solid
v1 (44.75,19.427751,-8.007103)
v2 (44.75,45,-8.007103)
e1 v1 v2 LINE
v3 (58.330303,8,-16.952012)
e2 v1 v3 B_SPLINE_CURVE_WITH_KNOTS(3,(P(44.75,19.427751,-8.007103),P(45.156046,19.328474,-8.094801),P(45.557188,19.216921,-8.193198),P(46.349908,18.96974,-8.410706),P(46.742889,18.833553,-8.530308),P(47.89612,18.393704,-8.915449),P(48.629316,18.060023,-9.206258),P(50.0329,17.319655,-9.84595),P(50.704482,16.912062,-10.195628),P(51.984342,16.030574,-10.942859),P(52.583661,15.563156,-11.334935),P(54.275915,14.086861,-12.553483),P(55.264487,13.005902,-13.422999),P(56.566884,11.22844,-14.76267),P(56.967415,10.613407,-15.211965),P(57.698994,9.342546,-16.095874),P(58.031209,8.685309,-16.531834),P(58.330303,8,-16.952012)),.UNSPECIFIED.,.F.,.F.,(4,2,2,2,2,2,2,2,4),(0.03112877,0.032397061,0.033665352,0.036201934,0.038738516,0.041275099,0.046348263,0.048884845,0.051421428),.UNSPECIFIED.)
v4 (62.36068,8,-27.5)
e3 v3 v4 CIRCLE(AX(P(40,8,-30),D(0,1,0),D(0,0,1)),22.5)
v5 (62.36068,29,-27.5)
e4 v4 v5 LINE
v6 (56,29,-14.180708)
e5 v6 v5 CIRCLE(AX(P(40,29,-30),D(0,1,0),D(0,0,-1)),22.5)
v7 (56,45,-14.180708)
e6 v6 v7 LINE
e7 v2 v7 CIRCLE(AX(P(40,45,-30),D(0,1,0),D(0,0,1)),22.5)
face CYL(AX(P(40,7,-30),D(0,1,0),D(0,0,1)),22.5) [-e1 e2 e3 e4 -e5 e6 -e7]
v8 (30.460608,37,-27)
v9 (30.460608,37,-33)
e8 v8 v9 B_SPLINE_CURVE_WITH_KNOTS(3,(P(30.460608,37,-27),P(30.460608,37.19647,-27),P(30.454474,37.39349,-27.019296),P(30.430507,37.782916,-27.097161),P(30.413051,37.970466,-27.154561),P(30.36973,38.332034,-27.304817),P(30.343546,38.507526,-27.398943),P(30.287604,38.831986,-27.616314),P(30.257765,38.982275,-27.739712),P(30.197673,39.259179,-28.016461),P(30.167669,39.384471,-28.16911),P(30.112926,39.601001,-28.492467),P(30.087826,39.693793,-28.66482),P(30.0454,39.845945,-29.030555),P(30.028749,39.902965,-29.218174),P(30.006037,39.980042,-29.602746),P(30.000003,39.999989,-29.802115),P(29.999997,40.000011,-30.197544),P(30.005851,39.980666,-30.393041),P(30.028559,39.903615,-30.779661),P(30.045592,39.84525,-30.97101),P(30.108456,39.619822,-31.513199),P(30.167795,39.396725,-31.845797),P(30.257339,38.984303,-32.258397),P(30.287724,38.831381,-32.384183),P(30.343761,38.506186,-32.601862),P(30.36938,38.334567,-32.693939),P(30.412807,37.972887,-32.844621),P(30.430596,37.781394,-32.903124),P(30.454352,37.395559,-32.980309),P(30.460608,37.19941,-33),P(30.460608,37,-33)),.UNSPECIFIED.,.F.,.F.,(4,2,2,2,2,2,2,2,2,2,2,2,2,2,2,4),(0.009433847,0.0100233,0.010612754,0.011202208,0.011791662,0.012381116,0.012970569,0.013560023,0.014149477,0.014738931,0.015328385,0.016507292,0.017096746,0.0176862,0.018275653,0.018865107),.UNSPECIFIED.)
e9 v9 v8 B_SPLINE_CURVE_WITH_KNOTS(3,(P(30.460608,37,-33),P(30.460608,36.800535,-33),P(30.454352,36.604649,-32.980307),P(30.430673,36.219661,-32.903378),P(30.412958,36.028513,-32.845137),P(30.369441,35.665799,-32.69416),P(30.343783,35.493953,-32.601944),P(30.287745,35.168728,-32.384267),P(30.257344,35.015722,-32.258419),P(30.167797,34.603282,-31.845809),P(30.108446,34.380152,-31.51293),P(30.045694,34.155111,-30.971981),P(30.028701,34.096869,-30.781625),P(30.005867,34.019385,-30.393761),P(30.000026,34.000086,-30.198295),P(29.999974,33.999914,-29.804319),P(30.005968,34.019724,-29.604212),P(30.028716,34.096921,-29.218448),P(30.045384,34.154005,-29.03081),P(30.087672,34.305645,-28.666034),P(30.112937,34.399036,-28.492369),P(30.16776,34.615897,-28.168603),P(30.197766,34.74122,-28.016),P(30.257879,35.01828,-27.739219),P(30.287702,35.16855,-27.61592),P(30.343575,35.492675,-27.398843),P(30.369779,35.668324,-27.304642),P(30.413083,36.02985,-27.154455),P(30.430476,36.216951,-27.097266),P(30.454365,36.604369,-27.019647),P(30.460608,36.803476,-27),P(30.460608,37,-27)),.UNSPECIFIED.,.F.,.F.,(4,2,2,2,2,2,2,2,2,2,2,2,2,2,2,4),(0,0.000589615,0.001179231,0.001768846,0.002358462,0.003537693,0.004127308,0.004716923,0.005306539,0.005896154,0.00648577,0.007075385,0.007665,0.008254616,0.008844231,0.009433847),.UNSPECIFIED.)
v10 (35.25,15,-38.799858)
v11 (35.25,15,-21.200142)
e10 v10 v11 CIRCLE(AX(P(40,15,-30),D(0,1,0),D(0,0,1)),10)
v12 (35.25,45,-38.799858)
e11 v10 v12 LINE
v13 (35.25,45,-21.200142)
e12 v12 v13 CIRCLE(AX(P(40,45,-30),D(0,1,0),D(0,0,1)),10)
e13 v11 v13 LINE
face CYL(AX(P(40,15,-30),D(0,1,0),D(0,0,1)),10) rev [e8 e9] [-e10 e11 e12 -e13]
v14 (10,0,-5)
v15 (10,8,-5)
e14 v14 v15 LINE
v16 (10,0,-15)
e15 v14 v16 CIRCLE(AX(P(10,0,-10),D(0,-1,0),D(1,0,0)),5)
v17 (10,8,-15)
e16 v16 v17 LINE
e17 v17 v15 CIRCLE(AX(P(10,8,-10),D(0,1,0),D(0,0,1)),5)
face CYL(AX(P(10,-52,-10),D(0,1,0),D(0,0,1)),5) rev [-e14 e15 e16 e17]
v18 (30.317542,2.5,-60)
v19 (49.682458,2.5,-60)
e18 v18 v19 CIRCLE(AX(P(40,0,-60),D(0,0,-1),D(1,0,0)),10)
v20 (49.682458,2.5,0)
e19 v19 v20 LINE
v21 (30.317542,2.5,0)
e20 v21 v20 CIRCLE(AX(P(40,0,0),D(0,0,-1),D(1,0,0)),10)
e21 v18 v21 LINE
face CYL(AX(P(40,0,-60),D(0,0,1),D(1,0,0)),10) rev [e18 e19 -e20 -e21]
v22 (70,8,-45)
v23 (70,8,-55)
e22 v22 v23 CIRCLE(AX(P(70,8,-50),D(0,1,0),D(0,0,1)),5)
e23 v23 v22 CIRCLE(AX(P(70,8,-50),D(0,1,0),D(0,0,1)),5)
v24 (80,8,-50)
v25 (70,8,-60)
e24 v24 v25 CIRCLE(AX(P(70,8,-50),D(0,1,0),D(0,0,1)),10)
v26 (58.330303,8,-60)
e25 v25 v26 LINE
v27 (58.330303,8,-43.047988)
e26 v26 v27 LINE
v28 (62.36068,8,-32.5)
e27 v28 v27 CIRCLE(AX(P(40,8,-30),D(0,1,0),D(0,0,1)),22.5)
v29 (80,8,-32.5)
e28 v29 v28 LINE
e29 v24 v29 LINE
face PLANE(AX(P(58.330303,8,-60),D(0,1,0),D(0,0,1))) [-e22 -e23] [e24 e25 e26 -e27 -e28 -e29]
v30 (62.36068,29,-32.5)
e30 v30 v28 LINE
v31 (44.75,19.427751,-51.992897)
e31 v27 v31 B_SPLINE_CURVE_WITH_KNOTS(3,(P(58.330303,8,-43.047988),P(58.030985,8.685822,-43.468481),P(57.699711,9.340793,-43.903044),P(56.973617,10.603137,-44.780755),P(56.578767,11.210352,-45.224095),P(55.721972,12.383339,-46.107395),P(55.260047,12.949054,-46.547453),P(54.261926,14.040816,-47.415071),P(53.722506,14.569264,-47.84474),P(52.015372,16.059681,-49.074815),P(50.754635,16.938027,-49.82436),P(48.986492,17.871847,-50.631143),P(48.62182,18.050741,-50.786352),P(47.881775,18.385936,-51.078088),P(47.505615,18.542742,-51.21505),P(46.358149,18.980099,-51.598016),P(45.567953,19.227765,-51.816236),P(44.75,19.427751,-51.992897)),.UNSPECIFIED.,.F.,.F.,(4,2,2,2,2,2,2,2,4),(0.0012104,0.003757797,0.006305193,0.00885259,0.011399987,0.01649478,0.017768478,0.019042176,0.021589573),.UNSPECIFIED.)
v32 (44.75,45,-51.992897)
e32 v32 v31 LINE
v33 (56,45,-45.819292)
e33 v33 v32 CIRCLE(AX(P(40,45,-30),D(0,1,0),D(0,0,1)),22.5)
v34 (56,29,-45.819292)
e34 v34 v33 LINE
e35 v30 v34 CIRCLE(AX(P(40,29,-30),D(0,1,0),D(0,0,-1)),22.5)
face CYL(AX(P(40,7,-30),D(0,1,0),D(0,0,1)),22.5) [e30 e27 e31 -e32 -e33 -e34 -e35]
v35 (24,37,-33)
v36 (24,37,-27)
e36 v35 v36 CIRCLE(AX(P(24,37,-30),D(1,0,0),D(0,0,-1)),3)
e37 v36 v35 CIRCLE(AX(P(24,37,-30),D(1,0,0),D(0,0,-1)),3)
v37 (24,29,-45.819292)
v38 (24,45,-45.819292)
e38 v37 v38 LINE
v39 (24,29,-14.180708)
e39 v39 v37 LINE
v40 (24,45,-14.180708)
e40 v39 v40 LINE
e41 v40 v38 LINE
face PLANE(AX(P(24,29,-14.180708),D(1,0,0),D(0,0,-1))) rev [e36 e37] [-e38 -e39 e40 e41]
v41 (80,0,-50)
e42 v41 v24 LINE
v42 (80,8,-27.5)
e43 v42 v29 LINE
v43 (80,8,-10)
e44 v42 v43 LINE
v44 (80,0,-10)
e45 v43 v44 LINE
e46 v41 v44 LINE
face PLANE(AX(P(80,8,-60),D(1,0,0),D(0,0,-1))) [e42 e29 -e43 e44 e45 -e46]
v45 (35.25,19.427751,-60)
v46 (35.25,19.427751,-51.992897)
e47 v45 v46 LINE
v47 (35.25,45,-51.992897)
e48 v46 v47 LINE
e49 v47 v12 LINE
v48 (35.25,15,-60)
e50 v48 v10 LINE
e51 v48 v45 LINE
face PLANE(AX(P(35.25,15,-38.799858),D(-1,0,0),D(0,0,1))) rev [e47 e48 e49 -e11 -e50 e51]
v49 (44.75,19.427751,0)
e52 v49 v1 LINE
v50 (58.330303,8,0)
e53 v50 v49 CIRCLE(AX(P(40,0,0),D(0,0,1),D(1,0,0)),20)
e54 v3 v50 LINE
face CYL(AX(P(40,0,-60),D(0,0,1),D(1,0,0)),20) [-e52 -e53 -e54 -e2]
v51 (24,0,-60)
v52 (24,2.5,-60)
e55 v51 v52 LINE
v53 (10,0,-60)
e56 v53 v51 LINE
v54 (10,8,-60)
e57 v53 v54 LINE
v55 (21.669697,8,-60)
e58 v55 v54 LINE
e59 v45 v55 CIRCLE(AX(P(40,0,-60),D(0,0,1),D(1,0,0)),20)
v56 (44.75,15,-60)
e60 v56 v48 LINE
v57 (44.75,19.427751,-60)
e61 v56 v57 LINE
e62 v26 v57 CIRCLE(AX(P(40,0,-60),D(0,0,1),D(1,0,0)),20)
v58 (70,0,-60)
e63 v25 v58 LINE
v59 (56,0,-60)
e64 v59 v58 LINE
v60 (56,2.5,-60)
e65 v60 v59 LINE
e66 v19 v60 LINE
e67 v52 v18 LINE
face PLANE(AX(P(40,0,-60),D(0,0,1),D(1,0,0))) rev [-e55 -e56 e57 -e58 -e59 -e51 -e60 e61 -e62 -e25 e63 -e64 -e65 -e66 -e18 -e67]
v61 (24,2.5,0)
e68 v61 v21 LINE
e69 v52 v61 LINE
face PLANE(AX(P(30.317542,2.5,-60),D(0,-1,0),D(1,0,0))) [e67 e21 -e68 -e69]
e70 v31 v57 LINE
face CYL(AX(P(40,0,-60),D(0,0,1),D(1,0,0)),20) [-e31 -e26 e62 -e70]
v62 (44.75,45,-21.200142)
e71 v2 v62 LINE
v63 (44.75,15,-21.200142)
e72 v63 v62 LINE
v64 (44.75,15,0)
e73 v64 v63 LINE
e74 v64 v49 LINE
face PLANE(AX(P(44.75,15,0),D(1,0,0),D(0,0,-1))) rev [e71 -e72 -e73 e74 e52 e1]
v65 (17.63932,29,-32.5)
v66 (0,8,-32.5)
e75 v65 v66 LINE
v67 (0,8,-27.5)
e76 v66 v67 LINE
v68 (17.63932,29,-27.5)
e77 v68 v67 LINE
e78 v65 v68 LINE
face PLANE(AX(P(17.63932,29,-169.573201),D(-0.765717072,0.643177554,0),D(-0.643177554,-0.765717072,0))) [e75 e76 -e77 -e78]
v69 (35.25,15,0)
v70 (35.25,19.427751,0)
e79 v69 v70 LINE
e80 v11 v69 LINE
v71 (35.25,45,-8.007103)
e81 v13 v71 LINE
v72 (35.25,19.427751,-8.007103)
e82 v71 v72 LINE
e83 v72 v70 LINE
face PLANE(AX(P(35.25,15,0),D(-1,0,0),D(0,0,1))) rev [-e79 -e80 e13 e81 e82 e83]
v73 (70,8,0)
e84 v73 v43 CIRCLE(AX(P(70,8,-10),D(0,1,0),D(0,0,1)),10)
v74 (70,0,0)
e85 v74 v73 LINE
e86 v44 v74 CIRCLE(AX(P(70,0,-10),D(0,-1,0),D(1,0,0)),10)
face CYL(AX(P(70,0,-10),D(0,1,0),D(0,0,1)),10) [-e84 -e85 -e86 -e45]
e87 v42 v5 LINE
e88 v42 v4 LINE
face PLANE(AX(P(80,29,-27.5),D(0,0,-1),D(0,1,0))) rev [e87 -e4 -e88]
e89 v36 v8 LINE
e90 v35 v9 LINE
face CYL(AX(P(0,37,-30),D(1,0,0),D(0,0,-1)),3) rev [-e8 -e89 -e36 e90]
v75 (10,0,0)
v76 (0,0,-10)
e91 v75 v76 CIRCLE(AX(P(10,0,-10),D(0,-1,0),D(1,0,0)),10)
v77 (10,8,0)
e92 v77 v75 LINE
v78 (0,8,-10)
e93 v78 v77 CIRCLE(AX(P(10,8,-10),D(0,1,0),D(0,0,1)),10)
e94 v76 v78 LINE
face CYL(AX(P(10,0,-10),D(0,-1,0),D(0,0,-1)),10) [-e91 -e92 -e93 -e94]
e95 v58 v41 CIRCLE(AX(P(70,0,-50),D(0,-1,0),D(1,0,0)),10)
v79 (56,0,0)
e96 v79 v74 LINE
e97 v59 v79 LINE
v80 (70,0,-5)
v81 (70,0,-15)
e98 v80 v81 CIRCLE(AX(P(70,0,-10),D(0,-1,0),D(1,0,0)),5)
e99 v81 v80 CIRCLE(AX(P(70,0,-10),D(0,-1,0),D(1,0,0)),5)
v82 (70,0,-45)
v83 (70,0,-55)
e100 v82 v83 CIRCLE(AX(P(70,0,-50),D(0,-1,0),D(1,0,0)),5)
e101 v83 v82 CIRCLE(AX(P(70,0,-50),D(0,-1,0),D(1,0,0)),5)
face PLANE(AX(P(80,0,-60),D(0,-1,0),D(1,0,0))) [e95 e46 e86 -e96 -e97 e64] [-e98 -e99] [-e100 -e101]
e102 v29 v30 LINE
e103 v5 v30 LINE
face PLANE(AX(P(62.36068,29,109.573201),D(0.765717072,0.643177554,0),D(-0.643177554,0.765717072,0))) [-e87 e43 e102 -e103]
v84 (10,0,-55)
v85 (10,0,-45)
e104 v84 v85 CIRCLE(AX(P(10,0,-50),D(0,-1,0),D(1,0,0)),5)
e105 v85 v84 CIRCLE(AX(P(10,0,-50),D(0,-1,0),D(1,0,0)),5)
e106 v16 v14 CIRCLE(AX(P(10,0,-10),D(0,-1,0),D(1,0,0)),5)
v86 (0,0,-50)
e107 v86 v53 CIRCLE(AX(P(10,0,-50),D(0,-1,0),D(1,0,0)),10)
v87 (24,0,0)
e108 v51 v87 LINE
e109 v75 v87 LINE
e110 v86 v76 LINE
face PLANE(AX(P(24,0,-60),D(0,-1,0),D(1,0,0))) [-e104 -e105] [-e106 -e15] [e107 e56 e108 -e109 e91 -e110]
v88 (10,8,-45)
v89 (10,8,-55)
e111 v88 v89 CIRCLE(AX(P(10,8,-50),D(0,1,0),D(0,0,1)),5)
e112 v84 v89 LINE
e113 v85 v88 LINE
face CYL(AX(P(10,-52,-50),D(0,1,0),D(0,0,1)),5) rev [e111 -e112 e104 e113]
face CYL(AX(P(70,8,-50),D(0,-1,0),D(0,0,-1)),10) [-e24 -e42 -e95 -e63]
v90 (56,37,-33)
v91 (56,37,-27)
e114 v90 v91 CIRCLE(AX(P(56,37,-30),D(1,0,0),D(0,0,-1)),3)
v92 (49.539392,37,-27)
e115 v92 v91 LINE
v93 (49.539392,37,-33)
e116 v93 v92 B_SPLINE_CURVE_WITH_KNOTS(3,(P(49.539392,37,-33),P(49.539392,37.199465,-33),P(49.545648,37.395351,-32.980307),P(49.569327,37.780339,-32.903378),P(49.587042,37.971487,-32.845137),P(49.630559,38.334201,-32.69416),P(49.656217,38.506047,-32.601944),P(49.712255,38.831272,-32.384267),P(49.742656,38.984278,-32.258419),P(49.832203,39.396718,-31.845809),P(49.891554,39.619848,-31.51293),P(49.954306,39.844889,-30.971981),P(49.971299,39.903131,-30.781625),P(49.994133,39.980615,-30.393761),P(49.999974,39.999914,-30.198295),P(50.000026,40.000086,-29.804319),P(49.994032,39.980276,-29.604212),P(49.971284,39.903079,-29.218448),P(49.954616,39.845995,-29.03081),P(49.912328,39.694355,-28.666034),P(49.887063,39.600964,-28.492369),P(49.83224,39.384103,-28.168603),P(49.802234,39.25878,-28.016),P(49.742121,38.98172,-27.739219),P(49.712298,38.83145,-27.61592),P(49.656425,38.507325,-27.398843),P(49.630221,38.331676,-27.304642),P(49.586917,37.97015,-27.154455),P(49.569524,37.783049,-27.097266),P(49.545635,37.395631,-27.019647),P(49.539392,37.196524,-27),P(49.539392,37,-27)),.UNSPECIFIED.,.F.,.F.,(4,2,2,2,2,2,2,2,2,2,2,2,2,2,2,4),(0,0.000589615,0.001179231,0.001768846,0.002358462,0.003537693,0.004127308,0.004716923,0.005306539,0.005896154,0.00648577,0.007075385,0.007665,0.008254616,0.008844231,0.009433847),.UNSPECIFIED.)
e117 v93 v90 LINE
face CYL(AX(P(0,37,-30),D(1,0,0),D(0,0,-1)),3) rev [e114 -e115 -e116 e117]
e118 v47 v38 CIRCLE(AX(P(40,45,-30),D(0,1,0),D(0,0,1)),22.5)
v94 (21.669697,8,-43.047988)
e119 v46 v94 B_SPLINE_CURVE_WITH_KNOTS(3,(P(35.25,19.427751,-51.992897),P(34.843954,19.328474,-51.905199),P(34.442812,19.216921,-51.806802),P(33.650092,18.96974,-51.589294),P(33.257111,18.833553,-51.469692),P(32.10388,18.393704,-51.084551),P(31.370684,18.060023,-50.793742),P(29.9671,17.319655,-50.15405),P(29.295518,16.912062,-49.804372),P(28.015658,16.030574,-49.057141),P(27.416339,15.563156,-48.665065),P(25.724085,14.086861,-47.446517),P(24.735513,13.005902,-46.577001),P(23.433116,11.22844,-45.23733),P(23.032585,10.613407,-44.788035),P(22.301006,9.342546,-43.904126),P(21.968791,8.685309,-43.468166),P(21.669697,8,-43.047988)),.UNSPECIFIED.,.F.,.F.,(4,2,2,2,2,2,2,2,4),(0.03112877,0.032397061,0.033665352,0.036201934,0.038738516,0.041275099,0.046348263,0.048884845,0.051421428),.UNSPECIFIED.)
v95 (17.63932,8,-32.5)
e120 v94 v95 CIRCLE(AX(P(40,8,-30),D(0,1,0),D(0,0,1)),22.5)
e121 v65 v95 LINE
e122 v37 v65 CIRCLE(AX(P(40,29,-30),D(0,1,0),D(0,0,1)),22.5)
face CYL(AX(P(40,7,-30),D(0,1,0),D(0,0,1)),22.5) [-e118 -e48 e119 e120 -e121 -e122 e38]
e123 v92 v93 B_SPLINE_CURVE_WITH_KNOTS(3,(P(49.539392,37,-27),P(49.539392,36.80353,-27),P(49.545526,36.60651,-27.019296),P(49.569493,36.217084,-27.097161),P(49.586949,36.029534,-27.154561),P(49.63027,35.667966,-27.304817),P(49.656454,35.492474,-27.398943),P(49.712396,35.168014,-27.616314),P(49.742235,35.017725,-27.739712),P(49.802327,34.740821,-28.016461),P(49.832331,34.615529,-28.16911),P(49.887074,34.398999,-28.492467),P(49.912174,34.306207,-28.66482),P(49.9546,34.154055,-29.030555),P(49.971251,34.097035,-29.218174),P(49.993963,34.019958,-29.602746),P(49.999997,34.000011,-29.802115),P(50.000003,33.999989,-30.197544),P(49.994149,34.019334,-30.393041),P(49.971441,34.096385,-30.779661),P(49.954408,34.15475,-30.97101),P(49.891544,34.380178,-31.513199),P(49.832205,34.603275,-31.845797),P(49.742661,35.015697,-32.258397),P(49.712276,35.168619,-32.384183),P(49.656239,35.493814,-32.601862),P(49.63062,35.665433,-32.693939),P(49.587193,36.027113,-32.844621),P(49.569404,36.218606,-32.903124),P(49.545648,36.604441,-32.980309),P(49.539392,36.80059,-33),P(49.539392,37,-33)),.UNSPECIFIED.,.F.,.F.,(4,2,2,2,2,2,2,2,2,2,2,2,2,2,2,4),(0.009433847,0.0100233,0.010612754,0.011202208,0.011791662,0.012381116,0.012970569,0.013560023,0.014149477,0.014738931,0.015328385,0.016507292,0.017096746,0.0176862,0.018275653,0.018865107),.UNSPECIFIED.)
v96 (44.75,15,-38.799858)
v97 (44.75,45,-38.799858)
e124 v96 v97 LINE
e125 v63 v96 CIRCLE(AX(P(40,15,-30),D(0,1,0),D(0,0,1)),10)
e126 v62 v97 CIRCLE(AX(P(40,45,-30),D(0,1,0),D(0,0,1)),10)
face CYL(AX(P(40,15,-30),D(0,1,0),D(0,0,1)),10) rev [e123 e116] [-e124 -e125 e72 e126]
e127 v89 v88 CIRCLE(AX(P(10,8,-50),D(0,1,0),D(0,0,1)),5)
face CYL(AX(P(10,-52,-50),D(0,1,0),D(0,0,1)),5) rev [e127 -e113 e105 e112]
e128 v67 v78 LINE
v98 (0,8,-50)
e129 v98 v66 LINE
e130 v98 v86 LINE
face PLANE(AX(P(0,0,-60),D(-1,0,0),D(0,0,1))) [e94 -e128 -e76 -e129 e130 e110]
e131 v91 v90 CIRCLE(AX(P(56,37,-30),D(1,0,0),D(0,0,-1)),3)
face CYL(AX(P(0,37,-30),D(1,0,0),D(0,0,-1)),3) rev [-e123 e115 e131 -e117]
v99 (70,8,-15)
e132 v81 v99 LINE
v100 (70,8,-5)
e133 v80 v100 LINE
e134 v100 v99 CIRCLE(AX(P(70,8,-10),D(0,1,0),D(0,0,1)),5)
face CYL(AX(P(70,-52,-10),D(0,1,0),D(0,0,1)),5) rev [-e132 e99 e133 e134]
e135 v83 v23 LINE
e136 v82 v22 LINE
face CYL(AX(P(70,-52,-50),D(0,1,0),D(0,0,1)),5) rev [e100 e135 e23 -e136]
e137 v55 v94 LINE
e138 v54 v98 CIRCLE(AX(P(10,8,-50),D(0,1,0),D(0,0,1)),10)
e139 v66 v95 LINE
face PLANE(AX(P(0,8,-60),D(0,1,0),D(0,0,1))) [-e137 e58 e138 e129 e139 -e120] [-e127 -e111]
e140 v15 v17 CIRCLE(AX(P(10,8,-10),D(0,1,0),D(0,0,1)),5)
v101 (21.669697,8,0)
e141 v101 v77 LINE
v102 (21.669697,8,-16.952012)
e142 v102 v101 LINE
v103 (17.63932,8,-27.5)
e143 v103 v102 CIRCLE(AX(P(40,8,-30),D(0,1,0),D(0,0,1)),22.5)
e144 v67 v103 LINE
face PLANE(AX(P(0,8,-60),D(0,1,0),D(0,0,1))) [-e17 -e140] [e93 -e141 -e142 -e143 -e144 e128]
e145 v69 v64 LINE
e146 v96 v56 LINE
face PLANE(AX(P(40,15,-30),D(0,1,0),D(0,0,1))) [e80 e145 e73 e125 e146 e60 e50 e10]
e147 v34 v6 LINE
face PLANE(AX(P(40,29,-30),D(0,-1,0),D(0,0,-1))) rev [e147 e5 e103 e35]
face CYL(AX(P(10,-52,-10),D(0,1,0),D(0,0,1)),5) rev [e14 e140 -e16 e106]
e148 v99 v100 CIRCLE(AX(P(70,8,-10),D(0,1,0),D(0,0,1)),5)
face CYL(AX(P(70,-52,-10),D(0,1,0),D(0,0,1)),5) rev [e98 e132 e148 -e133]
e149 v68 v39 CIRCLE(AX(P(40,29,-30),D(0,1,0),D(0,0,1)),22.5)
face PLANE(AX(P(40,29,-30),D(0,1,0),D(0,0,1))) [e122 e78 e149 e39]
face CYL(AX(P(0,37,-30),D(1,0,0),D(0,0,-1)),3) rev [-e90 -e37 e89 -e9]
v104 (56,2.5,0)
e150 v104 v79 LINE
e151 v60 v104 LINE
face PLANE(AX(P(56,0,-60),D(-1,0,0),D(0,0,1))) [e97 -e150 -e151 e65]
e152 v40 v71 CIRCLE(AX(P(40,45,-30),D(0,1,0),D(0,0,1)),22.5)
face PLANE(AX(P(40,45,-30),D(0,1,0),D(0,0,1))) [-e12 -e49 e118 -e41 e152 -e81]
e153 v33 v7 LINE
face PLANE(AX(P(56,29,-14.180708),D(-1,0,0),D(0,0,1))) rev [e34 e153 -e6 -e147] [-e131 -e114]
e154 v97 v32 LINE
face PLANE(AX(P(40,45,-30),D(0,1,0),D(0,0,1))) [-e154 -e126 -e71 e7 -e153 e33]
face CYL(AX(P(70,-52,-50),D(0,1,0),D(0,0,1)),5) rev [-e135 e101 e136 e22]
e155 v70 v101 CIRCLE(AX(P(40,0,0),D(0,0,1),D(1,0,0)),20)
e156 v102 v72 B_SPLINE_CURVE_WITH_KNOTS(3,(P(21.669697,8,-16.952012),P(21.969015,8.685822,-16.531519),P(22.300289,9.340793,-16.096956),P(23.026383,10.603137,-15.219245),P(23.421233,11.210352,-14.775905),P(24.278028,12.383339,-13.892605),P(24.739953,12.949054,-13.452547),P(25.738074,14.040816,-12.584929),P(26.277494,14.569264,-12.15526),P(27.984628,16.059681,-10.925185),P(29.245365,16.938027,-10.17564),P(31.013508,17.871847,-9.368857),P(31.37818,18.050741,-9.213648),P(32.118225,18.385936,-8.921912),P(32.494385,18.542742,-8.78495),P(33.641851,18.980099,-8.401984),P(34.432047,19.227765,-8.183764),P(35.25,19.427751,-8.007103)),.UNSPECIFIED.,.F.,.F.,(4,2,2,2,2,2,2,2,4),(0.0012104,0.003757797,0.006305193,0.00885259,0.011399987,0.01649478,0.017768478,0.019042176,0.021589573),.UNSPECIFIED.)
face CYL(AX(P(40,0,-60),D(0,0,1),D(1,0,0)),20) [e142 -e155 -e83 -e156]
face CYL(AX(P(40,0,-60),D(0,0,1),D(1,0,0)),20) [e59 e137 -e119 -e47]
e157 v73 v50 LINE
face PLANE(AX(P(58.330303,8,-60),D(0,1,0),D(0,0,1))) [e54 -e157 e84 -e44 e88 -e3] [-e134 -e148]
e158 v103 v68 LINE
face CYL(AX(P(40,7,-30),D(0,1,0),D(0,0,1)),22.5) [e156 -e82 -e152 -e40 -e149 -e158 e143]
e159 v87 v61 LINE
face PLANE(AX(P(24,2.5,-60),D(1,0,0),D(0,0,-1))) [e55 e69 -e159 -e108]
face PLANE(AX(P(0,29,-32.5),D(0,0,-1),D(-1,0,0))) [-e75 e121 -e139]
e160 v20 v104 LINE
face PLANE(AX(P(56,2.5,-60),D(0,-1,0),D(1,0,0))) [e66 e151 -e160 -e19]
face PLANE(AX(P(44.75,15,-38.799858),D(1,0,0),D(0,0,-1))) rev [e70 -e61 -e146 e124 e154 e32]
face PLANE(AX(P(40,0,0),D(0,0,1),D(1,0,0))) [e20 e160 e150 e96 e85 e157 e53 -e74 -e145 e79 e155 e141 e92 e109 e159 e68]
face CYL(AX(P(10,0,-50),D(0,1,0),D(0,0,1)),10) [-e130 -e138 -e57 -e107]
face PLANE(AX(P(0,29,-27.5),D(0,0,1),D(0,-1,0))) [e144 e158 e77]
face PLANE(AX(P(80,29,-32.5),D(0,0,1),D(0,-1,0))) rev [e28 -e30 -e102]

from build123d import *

# Parameters (mm, degrees)
BASE_BODY_DEPTH             = 60
VERTICAL_BOSS_SKETCH_R      = 22.5
VERTICAL_BOSS_40_DEPTH      = 38
BASE_HALF_BORE_SKETCH_R     = 10
BASE_HALF_BORE_20_DEPTH     = 60
BASE_CORNER_FILLETS_R10_R   = 10
MOUNTING_HOLES_SKETCH_R     = 5
MOUNTING_HOLES_4X_10_DEPTH  = 60
RIB_PROFILE_CUT_DEPTH       = 30
BOSS_UPPER_BORE_CUT_DEPTH   = 16
BOSS_LOWER_BORE_SKETCH_R    = 3
BOSS_LOWER_BORE_CUT_DEPTH   = 94.600213787
CLAMP_LUG_X62_SKETCH_W      = 5
CLAMP_LUG_X62_SKETCH_H      = 21
CLAMP_LUG_X62_DEPTH         = 18
LUG_X62_HOLE_CUT_DEPTH      = 98.37171055
LUG_X62_HOLE_CUT_DEPTH_BACK = 18
CLAMP_LUG_X18_SKETCH_W      = 5
CLAMP_LUG_X18_SKETCH_H      = 21
CLAMP_LUG_X18_DEPTH         = 18
LUG_X18_HOLE_CUT_DEPTH      = 98.37171055
LUG_X18_HOLE_CUT_DEPTH_BACK = 18


with BuildPart() as part:
    # Base Profile Sketch → Base Body (new body)
    with BuildSketch(Plane.XY):
        with BuildLine():
            Line((0, 0), (0, 8))
            Line((0, 8), (21.66969722, 8))
            ThreePointArc((21.66969722, 8), (40, 20), (58.33030278, 8))
            Line((58.33030278, 8), (80, 8))
            Line((80, 8), (80, 0))
            Line((80, 0), (56, 0))
            Line((56, 0), (56, 2.5))
            Line((56, 2.5), (49.682458366, 2.5))
            ThreePointArc((49.682458366, 2.5), (40, 10), (30.317541634, 2.5))
            Line((30.317541634, 2.5), (24, 2.5))
            Line((24, 2.5), (24, 0))
            Line((24, 0), (0, 0))
        make_face()
    extrude(amount=-BASE_BODY_DEPTH)

    # Vertical Boss Sketch → Vertical Boss Ø40 (add)
    with BuildSketch(Plane(origin=(0, 45, 0), x_dir=(1, 0, 0), z_dir=(0, 1, 0))):
        with Locations(Location((40, 30, 0), (0, 0, 270))):
            Circle(VERTICAL_BOSS_SKETCH_R)
    extrude(amount=-VERTICAL_BOSS_40_DEPTH)

    # Base Half Bore Sketch → Base Half Bore Ø20 (cut)
    with BuildSketch(Plane.XY):
        with Locations((40, 0)):
            Circle(BASE_HALF_BORE_SKETCH_R)
    extrude(amount=-BASE_HALF_BORE_20_DEPTH, mode=Mode.SUBTRACT)

    # Base Corner Fillets R10
    base_corner_fillets_r10_edges = [part.edges().sort_by_distance(p)[0] for p in [
        (0, 4, 0),
        (80, 4, 0),
        (80, 4, -60),
        (0, 4, -60),
    ]]
    fillet(base_corner_fillets_r10_edges, radius=BASE_CORNER_FILLETS_R10_R)

    # Mounting Holes Sketch → Mounting Holes 4xØ10 (cut)
    with BuildSketch(Plane(origin=(0, 8, 0), x_dir=(1, 0, 0), z_dir=(0, 1, 0))):
        with Locations(Location((70, 50, 0), (0, 0, 270))):
            Circle(MOUNTING_HOLES_SKETCH_R)
        with Locations(Location((70, 10, 0), (0, 0, 270))):
            Circle(MOUNTING_HOLES_SKETCH_R)
        with Locations(Location((10, 10, 0), (0, 0, 270))):
            Circle(MOUNTING_HOLES_SKETCH_R)
        with Locations(Location((10, 50, 0), (0, 0, 270))):
            Circle(MOUNTING_HOLES_SKETCH_R)
    extrude(amount=-MOUNTING_HOLES_4X_10_DEPTH, mode=Mode.SUBTRACT)

    # Rib Profile Sketch → Rib Profile Cut (cut)
    with BuildSketch(Plane(origin=(0, 45, 0), x_dir=(1, 0, 0), z_dir=(0, 1, 0))):
        with BuildLine():
            Line((35.25, 38.799857953), (35.25, 60))
            Line((35.25, 60), (44.75, 60))
            Line((44.75, 60), (44.75, 38.799857953))
            ThreePointArc((44.75, 38.799857953), (50, 30), (44.75, 21.200142047))
            Line((44.75, 21.200142047), (44.75, 0))
            Line((44.75, 0), (35.25, 0))
            Line((35.25, 0), (35.25, 21.200142047))
            ThreePointArc((35.25, 21.200142047), (30, 30), (35.25, 38.799857953))
        make_face()
    extrude(amount=-RIB_PROFILE_CUT_DEPTH, mode=Mode.SUBTRACT)

    # Boss Upper Bore Sketch → Boss Upper Bore Cut (cut)
    with BuildSketch(Plane(origin=(0, 45, 0), x_dir=(1, 0, 0), z_dir=(0, 1, 0))):
        with BuildLine():
            Line((56, 14.18070798), (56, 45.81929202))
            ThreePointArc((56, 45.81929202), (62.5, 30), (56, 14.18070798))
        make_face()
        with BuildLine():
            Line((24, 14.18070798), (24, 45.81929202))
            ThreePointArc((24, 45.81929202), (17.5, 30), (24, 14.18070798))
        make_face()
    extrude(amount=-BOSS_UPPER_BORE_CUT_DEPTH, mode=Mode.SUBTRACT)

    # Boss Lower Bore Sketch → Boss Lower Bore Cut (cut, through all)
    with BuildSketch(Plane(origin=(56, 0, 0), x_dir=(0, 0, -1), z_dir=(1, 0, 0))):
        with Locations((30, 37)):
            Circle(BOSS_LOWER_BORE_SKETCH_R)
    extrude(amount=-BOSS_LOWER_BORE_CUT_DEPTH, mode=Mode.SUBTRACT)

    # Clamp Lug X62 Sketch → Clamp Lug X62 (add)
    with BuildSketch(Plane(origin=(62, 0, 0), x_dir=(0, 0, -1), z_dir=(1, 0, 0))):
        with Locations((30, 18.5)):
            Rectangle(CLAMP_LUG_X62_SKETCH_W, CLAMP_LUG_X62_SKETCH_H)
    extrude(amount=CLAMP_LUG_X62_DEPTH)

    # Lug X62 Hole Sketch → Lug X62 Hole Cut (cut, two sides: drawn at the far end of the back side and taken through both)
    with BuildSketch(Plane.XY.offset(-27.5).offset(-LUG_X62_HOLE_CUT_DEPTH_BACK)):
        Polygon((80, 29), (62.360679775, 29), (80, 8), align=None)
    extrude(amount=LUG_X62_HOLE_CUT_DEPTH + LUG_X62_HOLE_CUT_DEPTH_BACK, mode=Mode.SUBTRACT)

    # Clamp Lug X18 Sketch → Clamp Lug X18 (add)
    with BuildSketch(Plane(origin=(18, 0, 0), x_dir=(0, 0, -1), z_dir=(1, 0, 0))):
        with Locations((30, 18.5)):
            Rectangle(CLAMP_LUG_X18_SKETCH_W, CLAMP_LUG_X18_SKETCH_H)
    extrude(amount=-CLAMP_LUG_X18_DEPTH)

    # Lug X18 Hole Sketch → Lug X18 Hole Cut (cut, two sides: drawn at the far end of the back side and taken through both)
    with BuildSketch(Plane(origin=(0, 0, -32.5), x_dir=(-1, 0, 0), z_dir=(0, 0, -1)).offset(-LUG_X18_HOLE_CUT_DEPTH_BACK)):
        Polygon((0, 29), (-17.639320225, 29), (0, 8), align=None)
    extrude(amount=LUG_X18_HOLE_CUT_DEPTH + LUG_X18_HOLE_CUT_DEPTH_BACK, mode=Mode.SUBTRACT)


solid = part.part
